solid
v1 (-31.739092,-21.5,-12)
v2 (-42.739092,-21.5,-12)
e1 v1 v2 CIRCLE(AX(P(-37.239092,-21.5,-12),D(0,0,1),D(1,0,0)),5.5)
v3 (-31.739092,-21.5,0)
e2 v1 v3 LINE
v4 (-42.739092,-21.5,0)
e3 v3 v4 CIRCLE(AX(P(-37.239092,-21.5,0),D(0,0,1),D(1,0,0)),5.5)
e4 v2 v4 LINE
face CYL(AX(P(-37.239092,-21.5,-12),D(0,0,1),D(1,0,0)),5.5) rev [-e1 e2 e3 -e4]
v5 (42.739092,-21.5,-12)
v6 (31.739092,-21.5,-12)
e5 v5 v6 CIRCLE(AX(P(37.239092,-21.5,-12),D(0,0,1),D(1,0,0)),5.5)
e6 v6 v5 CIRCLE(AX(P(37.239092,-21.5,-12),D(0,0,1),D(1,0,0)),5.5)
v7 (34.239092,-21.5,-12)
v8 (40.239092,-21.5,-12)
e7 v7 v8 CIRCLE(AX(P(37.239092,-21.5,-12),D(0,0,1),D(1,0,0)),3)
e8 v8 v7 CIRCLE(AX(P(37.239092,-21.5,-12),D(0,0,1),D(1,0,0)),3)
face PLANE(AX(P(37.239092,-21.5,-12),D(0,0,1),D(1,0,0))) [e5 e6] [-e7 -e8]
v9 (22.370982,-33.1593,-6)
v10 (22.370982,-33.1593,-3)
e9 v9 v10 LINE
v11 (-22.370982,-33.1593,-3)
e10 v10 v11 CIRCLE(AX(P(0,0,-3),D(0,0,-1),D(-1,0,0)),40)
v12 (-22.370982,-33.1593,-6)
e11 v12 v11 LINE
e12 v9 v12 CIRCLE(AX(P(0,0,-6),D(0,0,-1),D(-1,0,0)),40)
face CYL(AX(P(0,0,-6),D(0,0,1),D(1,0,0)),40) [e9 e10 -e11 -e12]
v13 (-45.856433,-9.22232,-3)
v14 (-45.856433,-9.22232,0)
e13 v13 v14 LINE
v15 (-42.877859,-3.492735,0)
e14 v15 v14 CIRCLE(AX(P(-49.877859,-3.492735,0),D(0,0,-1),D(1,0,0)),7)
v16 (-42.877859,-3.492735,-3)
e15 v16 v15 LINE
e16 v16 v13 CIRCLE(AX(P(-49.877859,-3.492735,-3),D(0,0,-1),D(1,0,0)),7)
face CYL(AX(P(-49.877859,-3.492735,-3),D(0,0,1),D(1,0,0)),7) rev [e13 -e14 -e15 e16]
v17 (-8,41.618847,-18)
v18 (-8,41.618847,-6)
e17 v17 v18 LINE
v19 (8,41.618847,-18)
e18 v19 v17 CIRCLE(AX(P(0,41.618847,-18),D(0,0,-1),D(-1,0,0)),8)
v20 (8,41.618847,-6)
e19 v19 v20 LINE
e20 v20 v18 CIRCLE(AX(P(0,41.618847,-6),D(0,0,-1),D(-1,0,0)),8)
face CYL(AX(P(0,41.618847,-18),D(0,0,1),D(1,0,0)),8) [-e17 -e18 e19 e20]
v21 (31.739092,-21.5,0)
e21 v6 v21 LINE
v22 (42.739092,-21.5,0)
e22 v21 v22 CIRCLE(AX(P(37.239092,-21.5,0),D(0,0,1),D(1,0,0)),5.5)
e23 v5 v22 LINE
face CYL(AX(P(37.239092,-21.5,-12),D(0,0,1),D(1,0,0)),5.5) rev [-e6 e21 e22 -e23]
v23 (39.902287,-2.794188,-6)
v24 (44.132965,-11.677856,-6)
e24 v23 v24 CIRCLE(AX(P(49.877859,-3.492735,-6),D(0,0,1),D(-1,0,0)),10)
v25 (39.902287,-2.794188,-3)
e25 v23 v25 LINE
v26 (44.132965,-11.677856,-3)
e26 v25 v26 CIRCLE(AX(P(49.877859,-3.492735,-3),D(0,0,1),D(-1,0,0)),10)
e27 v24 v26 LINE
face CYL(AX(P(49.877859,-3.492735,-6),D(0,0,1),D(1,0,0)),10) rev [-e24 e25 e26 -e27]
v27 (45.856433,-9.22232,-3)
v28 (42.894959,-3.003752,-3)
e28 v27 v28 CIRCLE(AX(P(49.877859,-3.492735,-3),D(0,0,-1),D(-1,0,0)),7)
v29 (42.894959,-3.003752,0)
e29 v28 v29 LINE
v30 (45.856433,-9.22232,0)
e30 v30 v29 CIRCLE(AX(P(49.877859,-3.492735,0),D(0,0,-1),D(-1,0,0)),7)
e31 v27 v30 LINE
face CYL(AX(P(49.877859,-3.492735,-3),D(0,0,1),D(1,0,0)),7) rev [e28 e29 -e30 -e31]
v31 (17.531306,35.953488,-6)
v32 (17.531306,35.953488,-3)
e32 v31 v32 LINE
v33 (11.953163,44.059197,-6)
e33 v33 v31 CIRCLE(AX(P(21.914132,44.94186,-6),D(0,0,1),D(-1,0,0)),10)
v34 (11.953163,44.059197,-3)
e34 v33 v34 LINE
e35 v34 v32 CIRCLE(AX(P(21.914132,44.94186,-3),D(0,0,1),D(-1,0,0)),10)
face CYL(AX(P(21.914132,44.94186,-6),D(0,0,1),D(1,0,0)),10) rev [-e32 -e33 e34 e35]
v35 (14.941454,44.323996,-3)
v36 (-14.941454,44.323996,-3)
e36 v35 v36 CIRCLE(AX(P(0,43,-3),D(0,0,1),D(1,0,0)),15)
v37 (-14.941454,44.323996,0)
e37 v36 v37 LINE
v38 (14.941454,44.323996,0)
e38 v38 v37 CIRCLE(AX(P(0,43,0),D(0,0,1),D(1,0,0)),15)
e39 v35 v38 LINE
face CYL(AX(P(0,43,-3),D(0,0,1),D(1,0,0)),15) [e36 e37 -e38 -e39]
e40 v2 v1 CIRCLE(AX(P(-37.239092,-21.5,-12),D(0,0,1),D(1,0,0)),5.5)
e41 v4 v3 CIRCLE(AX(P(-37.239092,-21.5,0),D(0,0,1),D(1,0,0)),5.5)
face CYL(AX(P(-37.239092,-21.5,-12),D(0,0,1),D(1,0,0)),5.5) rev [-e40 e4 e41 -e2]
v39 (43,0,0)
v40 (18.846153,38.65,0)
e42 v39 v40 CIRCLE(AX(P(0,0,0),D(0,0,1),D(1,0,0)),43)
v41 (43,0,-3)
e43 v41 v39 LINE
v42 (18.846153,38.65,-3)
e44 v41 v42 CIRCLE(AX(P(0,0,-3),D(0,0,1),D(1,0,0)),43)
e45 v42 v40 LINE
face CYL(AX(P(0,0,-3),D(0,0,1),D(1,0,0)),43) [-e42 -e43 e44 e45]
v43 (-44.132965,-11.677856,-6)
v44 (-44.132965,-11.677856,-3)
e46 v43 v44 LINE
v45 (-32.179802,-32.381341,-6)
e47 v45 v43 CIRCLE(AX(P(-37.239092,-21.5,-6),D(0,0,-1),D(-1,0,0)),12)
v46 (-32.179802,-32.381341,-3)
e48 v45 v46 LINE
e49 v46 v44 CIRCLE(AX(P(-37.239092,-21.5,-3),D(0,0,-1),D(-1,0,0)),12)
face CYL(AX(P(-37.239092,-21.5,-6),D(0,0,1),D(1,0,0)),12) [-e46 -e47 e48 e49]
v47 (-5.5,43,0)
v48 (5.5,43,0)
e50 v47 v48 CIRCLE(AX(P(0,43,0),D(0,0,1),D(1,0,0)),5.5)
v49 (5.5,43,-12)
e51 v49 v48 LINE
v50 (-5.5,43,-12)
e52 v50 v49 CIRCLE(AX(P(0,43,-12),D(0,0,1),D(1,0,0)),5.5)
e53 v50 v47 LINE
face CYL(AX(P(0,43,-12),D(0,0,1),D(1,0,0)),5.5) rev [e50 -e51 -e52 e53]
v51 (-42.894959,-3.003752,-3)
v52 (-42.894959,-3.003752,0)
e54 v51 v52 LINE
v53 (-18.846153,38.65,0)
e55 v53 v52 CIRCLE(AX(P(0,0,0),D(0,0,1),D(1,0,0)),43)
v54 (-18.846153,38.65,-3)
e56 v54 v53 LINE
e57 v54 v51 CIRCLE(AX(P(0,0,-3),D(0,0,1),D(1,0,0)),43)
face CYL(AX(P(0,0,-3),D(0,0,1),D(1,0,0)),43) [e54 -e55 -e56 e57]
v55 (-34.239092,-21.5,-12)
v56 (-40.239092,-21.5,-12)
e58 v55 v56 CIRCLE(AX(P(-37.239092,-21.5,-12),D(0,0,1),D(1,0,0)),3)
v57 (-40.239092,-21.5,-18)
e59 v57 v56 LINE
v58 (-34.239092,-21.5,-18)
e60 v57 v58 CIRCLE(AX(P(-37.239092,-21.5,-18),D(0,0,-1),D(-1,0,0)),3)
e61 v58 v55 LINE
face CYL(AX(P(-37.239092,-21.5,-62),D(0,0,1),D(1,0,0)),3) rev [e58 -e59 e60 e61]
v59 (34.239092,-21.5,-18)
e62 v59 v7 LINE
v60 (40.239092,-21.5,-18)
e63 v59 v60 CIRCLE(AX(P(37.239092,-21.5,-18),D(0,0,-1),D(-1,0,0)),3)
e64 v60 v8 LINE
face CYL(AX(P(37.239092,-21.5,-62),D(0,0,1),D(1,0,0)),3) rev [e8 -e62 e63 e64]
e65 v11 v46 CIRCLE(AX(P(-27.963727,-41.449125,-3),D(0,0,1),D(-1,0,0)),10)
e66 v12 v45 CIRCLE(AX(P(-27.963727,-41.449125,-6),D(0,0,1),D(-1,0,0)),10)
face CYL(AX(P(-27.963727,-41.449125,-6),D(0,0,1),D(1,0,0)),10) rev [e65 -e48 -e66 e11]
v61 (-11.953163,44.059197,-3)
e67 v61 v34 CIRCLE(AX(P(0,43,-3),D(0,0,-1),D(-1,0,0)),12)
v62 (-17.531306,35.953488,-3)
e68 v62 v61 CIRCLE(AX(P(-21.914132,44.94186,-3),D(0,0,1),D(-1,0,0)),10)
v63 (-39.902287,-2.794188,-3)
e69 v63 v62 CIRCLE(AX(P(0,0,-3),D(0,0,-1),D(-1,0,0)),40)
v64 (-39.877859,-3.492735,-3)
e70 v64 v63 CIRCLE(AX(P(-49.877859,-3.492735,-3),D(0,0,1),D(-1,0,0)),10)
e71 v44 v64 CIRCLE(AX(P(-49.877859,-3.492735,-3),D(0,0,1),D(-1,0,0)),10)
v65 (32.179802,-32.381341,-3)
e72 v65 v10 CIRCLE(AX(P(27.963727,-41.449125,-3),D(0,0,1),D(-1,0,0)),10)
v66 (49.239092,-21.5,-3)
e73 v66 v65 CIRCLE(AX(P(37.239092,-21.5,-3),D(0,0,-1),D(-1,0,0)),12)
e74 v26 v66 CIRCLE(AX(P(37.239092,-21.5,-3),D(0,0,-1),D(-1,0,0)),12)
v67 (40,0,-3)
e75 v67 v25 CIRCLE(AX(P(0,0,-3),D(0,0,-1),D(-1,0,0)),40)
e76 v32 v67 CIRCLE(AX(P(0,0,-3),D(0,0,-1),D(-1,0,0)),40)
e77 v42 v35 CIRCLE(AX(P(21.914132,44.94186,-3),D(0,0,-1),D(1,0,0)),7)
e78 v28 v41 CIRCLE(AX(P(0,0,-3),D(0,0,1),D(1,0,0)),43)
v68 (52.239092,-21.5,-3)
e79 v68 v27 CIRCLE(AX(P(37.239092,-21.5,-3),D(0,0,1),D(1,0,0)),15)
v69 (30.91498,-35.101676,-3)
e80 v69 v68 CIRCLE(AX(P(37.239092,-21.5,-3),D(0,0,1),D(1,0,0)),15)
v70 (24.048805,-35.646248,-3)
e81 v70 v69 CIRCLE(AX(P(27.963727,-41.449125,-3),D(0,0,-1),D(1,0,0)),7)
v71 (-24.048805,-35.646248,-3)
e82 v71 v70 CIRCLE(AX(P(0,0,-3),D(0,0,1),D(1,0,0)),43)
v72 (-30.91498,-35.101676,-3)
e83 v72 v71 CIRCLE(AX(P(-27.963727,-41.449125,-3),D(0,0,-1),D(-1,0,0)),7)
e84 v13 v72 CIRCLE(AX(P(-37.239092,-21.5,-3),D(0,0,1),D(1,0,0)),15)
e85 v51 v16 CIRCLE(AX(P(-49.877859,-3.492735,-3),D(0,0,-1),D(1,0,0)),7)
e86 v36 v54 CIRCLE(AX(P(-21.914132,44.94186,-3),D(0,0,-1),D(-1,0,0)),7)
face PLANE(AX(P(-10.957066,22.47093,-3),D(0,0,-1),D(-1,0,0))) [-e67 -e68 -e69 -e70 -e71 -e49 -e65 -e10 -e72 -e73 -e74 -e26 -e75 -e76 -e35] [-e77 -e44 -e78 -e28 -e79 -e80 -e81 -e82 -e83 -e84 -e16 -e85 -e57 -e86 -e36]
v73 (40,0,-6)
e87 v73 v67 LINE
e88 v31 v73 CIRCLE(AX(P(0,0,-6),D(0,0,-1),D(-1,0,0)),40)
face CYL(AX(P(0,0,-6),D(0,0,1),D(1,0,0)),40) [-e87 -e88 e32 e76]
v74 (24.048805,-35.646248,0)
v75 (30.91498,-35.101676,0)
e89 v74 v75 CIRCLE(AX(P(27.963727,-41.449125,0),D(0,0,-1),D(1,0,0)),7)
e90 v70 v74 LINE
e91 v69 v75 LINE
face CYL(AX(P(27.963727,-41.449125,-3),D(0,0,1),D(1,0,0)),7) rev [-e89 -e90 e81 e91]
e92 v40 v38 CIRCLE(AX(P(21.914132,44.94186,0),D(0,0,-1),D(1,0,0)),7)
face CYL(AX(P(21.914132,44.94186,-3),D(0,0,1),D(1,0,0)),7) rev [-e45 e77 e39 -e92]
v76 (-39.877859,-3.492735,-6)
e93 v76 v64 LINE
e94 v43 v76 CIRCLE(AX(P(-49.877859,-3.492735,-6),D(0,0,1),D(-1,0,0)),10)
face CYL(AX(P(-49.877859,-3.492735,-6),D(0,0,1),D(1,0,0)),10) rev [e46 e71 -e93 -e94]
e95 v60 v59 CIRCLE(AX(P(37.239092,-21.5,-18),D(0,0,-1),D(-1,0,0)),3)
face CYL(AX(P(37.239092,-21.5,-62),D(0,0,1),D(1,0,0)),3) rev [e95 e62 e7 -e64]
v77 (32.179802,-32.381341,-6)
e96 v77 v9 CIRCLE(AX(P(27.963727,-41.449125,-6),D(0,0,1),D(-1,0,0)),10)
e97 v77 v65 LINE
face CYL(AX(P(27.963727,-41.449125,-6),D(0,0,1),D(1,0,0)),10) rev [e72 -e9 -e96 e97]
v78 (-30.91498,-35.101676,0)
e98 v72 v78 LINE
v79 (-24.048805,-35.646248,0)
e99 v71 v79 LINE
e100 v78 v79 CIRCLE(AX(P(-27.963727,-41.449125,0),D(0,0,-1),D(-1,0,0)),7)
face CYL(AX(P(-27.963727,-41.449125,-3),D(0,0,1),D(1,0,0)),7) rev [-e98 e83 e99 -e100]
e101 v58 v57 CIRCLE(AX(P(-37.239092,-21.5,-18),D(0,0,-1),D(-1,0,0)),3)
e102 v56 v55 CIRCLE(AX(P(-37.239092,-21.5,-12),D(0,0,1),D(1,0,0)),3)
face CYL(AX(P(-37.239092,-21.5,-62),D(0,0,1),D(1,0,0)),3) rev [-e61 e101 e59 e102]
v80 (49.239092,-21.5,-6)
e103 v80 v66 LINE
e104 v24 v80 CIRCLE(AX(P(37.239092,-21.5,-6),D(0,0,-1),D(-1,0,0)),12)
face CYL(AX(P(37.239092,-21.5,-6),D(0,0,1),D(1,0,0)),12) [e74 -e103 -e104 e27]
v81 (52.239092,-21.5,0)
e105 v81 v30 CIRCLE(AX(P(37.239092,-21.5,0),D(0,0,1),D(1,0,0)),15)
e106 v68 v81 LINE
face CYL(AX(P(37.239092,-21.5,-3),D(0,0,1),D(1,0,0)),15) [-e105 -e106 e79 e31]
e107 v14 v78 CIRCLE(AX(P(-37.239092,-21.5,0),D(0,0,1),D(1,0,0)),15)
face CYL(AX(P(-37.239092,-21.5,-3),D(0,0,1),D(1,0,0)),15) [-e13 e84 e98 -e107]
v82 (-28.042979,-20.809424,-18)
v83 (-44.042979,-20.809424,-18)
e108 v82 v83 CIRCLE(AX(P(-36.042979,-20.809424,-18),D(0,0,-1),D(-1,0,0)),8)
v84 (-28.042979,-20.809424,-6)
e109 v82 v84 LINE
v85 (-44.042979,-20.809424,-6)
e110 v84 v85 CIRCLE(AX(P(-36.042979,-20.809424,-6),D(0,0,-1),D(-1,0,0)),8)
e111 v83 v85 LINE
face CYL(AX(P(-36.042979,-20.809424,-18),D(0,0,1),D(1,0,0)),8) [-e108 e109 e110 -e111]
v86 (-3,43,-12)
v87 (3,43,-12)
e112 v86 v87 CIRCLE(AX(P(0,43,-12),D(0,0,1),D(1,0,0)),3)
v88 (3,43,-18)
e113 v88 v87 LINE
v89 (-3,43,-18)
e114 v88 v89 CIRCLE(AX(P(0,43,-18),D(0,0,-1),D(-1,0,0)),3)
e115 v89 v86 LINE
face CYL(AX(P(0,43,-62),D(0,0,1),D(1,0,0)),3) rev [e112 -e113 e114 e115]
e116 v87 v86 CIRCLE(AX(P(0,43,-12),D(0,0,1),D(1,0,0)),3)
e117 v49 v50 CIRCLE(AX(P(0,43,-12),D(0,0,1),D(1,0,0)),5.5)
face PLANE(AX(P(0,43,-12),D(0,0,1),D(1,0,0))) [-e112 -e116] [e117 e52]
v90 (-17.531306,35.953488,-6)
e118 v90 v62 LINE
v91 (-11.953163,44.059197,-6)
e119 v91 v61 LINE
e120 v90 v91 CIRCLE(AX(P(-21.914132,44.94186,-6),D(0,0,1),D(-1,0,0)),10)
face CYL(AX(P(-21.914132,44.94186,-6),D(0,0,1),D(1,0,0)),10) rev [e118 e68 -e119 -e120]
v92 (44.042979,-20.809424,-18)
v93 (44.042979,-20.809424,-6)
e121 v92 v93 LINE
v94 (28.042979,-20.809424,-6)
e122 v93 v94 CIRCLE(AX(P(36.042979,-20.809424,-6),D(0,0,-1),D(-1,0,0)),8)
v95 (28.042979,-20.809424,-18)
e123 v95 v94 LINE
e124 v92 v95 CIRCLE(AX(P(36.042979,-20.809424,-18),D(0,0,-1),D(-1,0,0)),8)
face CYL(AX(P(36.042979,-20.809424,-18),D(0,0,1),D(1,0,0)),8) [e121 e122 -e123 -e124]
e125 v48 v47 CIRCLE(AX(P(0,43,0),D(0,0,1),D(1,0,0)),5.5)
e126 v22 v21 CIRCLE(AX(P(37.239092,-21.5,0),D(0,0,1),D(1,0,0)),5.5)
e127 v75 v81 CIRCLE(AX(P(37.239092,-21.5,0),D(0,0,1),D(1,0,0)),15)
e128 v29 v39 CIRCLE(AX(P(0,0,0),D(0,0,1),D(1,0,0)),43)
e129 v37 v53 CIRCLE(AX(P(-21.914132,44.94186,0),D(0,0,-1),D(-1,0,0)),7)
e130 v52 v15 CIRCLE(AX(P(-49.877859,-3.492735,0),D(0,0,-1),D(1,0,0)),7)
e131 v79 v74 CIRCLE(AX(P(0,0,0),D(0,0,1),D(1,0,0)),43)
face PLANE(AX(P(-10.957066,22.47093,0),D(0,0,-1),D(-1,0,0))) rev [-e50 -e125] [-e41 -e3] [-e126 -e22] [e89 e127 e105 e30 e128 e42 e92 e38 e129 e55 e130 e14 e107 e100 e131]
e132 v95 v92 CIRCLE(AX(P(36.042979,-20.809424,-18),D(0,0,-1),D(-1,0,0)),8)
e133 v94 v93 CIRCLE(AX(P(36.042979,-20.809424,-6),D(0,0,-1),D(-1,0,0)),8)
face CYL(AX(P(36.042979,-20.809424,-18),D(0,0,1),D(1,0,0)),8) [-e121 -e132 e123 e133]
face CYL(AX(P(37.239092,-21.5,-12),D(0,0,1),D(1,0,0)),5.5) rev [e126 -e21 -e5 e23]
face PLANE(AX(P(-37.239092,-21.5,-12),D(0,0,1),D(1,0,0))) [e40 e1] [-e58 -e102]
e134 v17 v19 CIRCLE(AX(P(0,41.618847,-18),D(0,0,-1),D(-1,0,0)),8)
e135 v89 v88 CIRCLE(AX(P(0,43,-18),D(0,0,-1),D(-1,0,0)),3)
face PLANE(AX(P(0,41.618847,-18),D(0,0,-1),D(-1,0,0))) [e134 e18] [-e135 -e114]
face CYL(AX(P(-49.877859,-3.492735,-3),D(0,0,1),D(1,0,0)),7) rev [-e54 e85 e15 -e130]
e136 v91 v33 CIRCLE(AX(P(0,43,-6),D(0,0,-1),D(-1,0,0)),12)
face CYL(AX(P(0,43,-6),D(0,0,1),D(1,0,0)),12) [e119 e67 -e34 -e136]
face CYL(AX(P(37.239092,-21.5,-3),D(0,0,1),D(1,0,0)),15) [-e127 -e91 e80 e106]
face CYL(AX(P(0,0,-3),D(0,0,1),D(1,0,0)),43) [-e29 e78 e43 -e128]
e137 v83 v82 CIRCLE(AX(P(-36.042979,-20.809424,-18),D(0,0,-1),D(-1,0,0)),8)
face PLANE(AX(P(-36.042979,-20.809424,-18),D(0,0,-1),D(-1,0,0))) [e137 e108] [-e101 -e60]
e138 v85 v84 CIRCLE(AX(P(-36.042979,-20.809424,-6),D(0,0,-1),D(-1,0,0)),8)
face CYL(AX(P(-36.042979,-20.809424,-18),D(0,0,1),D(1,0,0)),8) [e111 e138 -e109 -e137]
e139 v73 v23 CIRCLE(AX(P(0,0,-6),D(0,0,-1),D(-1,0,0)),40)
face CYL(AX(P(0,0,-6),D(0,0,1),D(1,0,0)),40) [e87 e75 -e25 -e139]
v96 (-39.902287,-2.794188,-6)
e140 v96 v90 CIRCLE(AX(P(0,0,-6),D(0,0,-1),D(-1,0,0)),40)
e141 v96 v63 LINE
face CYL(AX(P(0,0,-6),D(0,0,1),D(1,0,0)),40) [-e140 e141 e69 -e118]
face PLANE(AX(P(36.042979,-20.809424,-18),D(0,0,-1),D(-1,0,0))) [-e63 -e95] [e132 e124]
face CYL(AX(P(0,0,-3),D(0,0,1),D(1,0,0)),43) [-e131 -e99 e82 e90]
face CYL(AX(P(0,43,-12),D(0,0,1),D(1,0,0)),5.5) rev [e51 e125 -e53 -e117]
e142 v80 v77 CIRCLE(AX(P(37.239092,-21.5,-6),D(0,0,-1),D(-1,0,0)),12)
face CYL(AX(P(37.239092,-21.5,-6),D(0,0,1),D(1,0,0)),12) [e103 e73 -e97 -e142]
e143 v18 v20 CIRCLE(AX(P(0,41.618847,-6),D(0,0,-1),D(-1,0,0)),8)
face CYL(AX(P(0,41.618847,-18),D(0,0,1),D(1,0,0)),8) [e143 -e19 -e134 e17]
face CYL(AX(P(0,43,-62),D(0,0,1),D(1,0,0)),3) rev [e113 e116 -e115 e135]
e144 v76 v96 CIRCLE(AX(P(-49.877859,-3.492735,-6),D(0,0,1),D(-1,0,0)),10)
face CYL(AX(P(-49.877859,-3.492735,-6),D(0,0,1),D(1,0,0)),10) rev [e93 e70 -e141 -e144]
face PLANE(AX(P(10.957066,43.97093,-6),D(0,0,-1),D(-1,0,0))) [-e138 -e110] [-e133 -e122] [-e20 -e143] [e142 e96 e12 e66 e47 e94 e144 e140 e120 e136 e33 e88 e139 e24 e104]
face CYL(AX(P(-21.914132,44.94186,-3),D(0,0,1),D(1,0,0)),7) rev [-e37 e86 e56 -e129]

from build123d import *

# Parameters (mm, degrees)
FLANGE_PLATE_3MM_DEPTH          = 3
RAISED_LIP_3MM_DEPTH            = 3
BOSSES_3X_16_SKETCH_R           = 8
BOSSES_3X_16_DEPTH              = 12
MOUNTING_HOLES_SKETCH_R         = 5.5
MOUNTING_HOLES_SKETCH_R_2       = 3
HOLE_CUT_DEPTH_12_DEPTH         = 12
SKETCH4_2_R                     = 3
MOUNTING_HOLES_3X_THROUGH_DEPTH = 62


with BuildPart() as part:
    # Flange Plate Profile Sketch → Flange Plate 3mm (new body)
    with BuildSketch(Plane.XY):
        with BuildLine():
            ThreePointArc((-18.846153454, 38.65), (-37.239092363, 21.5), (-42.894958583, -3.003752345))
            ThreePointArc((-42.894958583, -3.003752345), (-43.557934635, -6.502479184), (-45.856433127, -9.222319513))
            ThreePointArc((-45.856433127, -9.222319513), (-50.229473419, -29), (-30.914979544, -35.101676259))
            ThreePointArc((-30.914979544, -35.101676259), (-27.410279478, -34.471038339), (-24.048805129, -35.646247655))
            ThreePointArc((-24.048805129, -35.646247655), (0, -43), (24.048805129, -35.646247655))
            ThreePointArc((24.048805129, -35.646247655), (27.410279478, -34.471038339), (30.914979544, -35.101676259))
            ThreePointArc((30.914979544, -35.101676259), (50.229473419, -29), (45.856433127, -9.222319513))
            ThreePointArc((45.856433127, -9.222319513), (43.557934635, -6.502479184), (42.894958583, -3.003752345))
            ThreePointArc((42.894958583, -3.003752345), (37.239092363, 21.5), (18.846153454, 38.65))
            ThreePointArc((18.846153454, 38.65), (16.147655157, 40.973517523), (14.941453584, 44.323995772))
            ThreePointArc((14.941453584, 44.323995772), (0, 58), (-14.941453584, 44.323995772))
            ThreePointArc((-14.941453584, 44.323995772), (-16.147655157, 40.973517523), (-18.846153454, 38.65))
        make_face()
    extrude(amount=-FLANGE_PLATE_3MM_DEPTH)

    # Raised Lip Sketch → Raised Lip 3mm (add)
    with BuildSketch(Plane(origin=(0, 0, -3), x_dir=(-1, 0, 0), z_dir=(0, 0, -1))):
        with BuildLine():
            ThreePointArc((11.953162867, 44.059196617), (13.676307972, 39.272799119), (17.531305538, 35.953488372))
            ThreePointArc((17.531305538, 35.953488372), (34.641016151, 20), (39.902287054, -2.794188228))
            ThreePointArc((39.902287054, -2.794188228), (40.8493957, -7.792369426), (44.132964974, -11.67785561))
            ThreePointArc((44.132964974, -11.67785561), (47.631397208, -27.5), (32.179802107, -32.381341007))
            ThreePointArc((32.179802107, -32.381341007), (27.173087728, -31.480429693), (22.370981516, -33.159300144))
            ThreePointArc((22.370981516, -33.159300144), (0, -40), (-22.370981516, -33.159300144))
            ThreePointArc((-22.370981516, -33.159300144), (-27.173087728, -31.480429693), (-32.179802107, -32.381341007))
            ThreePointArc((-32.179802107, -32.381341007), (-47.631397208, -27.5), (-44.132964974, -11.67785561))
            ThreePointArc((-44.132964974, -11.67785561), (-40.8493957, -7.792369426), (-39.902287054, -2.794188228))
            ThreePointArc((-39.902287054, -2.794188228), (-34.641016151, 20), (-17.531305538, 35.953488372))
            ThreePointArc((-17.531305538, 35.953488372), (-13.676307972, 39.272799119), (-11.953162867, 44.059196617))
            ThreePointArc((-11.953162867, 44.059196617), (0, 55), (11.953162867, 44.059196617))
        make_face()
    extrude(amount=RAISED_LIP_3MM_DEPTH)

    # Bosses 3x_16 Sketch → Bosses 3x_16 (add)
    with BuildSketch(Plane(origin=(0, 0, -6), x_dir=(-1, 0, 0), z_dir=(0, 0, -1))):
        with Locations((0, 41.618847382)):
            Circle(BOSSES_3X_16_SKETCH_R)
        with Locations((36.042979109, -20.809423691)):
            Circle(BOSSES_3X_16_SKETCH_R)
        with Locations((-36.042979109, -20.809423691)):
            Circle(BOSSES_3X_16_SKETCH_R)
    extrude(amount=BOSSES_3X_16_DEPTH)

    # Mounting Holes Sketch → Hole Cut Depth 12 (cut)
    # profile 1 of 3: a face of its own
    with BuildSketch(Plane.XY):
        with Locations((0, 43)):
            Circle(MOUNTING_HOLES_SKETCH_R)
        with Locations((0, 43)):
            Circle(MOUNTING_HOLES_SKETCH_R_2, mode=Mode.SUBTRACT)
    # profile 2 of 3: a face of its own
    with BuildSketch(Plane.XY):
        with Locations((37.239092363, -21.5)):
            Circle(MOUNTING_HOLES_SKETCH_R)
        with Locations((37.239092363, -21.5)):
            Circle(MOUNTING_HOLES_SKETCH_R_2, mode=Mode.SUBTRACT)
    # profile 3 of 3: a face of its own
    with BuildSketch(Plane.XY):
        with Locations((-37.239092363, -21.5)):
            Circle(MOUNTING_HOLES_SKETCH_R)
        with Locations((-37.239092363, -21.5)):
            Circle(MOUNTING_HOLES_SKETCH_R_2, mode=Mode.SUBTRACT)
    extrude(amount=-HOLE_CUT_DEPTH_12_DEPTH, mode=Mode.SUBTRACT)

    # Sketch4_2 → Mounting Holes 3x Through (cut)
    with BuildSketch(Plane.XY):
        with Locations((0, 43)):
            Circle(SKETCH4_2_R)
        with Locations((-37.239092363, -21.5)):
            Circle(SKETCH4_2_R)
        with Locations((37.239092363, -21.5)):
            Circle(SKETCH4_2_R)
    extrude(amount=-MOUNTING_HOLES_3X_THROUGH_DEPTH, mode=Mode.SUBTRACT)


solid = part.part
